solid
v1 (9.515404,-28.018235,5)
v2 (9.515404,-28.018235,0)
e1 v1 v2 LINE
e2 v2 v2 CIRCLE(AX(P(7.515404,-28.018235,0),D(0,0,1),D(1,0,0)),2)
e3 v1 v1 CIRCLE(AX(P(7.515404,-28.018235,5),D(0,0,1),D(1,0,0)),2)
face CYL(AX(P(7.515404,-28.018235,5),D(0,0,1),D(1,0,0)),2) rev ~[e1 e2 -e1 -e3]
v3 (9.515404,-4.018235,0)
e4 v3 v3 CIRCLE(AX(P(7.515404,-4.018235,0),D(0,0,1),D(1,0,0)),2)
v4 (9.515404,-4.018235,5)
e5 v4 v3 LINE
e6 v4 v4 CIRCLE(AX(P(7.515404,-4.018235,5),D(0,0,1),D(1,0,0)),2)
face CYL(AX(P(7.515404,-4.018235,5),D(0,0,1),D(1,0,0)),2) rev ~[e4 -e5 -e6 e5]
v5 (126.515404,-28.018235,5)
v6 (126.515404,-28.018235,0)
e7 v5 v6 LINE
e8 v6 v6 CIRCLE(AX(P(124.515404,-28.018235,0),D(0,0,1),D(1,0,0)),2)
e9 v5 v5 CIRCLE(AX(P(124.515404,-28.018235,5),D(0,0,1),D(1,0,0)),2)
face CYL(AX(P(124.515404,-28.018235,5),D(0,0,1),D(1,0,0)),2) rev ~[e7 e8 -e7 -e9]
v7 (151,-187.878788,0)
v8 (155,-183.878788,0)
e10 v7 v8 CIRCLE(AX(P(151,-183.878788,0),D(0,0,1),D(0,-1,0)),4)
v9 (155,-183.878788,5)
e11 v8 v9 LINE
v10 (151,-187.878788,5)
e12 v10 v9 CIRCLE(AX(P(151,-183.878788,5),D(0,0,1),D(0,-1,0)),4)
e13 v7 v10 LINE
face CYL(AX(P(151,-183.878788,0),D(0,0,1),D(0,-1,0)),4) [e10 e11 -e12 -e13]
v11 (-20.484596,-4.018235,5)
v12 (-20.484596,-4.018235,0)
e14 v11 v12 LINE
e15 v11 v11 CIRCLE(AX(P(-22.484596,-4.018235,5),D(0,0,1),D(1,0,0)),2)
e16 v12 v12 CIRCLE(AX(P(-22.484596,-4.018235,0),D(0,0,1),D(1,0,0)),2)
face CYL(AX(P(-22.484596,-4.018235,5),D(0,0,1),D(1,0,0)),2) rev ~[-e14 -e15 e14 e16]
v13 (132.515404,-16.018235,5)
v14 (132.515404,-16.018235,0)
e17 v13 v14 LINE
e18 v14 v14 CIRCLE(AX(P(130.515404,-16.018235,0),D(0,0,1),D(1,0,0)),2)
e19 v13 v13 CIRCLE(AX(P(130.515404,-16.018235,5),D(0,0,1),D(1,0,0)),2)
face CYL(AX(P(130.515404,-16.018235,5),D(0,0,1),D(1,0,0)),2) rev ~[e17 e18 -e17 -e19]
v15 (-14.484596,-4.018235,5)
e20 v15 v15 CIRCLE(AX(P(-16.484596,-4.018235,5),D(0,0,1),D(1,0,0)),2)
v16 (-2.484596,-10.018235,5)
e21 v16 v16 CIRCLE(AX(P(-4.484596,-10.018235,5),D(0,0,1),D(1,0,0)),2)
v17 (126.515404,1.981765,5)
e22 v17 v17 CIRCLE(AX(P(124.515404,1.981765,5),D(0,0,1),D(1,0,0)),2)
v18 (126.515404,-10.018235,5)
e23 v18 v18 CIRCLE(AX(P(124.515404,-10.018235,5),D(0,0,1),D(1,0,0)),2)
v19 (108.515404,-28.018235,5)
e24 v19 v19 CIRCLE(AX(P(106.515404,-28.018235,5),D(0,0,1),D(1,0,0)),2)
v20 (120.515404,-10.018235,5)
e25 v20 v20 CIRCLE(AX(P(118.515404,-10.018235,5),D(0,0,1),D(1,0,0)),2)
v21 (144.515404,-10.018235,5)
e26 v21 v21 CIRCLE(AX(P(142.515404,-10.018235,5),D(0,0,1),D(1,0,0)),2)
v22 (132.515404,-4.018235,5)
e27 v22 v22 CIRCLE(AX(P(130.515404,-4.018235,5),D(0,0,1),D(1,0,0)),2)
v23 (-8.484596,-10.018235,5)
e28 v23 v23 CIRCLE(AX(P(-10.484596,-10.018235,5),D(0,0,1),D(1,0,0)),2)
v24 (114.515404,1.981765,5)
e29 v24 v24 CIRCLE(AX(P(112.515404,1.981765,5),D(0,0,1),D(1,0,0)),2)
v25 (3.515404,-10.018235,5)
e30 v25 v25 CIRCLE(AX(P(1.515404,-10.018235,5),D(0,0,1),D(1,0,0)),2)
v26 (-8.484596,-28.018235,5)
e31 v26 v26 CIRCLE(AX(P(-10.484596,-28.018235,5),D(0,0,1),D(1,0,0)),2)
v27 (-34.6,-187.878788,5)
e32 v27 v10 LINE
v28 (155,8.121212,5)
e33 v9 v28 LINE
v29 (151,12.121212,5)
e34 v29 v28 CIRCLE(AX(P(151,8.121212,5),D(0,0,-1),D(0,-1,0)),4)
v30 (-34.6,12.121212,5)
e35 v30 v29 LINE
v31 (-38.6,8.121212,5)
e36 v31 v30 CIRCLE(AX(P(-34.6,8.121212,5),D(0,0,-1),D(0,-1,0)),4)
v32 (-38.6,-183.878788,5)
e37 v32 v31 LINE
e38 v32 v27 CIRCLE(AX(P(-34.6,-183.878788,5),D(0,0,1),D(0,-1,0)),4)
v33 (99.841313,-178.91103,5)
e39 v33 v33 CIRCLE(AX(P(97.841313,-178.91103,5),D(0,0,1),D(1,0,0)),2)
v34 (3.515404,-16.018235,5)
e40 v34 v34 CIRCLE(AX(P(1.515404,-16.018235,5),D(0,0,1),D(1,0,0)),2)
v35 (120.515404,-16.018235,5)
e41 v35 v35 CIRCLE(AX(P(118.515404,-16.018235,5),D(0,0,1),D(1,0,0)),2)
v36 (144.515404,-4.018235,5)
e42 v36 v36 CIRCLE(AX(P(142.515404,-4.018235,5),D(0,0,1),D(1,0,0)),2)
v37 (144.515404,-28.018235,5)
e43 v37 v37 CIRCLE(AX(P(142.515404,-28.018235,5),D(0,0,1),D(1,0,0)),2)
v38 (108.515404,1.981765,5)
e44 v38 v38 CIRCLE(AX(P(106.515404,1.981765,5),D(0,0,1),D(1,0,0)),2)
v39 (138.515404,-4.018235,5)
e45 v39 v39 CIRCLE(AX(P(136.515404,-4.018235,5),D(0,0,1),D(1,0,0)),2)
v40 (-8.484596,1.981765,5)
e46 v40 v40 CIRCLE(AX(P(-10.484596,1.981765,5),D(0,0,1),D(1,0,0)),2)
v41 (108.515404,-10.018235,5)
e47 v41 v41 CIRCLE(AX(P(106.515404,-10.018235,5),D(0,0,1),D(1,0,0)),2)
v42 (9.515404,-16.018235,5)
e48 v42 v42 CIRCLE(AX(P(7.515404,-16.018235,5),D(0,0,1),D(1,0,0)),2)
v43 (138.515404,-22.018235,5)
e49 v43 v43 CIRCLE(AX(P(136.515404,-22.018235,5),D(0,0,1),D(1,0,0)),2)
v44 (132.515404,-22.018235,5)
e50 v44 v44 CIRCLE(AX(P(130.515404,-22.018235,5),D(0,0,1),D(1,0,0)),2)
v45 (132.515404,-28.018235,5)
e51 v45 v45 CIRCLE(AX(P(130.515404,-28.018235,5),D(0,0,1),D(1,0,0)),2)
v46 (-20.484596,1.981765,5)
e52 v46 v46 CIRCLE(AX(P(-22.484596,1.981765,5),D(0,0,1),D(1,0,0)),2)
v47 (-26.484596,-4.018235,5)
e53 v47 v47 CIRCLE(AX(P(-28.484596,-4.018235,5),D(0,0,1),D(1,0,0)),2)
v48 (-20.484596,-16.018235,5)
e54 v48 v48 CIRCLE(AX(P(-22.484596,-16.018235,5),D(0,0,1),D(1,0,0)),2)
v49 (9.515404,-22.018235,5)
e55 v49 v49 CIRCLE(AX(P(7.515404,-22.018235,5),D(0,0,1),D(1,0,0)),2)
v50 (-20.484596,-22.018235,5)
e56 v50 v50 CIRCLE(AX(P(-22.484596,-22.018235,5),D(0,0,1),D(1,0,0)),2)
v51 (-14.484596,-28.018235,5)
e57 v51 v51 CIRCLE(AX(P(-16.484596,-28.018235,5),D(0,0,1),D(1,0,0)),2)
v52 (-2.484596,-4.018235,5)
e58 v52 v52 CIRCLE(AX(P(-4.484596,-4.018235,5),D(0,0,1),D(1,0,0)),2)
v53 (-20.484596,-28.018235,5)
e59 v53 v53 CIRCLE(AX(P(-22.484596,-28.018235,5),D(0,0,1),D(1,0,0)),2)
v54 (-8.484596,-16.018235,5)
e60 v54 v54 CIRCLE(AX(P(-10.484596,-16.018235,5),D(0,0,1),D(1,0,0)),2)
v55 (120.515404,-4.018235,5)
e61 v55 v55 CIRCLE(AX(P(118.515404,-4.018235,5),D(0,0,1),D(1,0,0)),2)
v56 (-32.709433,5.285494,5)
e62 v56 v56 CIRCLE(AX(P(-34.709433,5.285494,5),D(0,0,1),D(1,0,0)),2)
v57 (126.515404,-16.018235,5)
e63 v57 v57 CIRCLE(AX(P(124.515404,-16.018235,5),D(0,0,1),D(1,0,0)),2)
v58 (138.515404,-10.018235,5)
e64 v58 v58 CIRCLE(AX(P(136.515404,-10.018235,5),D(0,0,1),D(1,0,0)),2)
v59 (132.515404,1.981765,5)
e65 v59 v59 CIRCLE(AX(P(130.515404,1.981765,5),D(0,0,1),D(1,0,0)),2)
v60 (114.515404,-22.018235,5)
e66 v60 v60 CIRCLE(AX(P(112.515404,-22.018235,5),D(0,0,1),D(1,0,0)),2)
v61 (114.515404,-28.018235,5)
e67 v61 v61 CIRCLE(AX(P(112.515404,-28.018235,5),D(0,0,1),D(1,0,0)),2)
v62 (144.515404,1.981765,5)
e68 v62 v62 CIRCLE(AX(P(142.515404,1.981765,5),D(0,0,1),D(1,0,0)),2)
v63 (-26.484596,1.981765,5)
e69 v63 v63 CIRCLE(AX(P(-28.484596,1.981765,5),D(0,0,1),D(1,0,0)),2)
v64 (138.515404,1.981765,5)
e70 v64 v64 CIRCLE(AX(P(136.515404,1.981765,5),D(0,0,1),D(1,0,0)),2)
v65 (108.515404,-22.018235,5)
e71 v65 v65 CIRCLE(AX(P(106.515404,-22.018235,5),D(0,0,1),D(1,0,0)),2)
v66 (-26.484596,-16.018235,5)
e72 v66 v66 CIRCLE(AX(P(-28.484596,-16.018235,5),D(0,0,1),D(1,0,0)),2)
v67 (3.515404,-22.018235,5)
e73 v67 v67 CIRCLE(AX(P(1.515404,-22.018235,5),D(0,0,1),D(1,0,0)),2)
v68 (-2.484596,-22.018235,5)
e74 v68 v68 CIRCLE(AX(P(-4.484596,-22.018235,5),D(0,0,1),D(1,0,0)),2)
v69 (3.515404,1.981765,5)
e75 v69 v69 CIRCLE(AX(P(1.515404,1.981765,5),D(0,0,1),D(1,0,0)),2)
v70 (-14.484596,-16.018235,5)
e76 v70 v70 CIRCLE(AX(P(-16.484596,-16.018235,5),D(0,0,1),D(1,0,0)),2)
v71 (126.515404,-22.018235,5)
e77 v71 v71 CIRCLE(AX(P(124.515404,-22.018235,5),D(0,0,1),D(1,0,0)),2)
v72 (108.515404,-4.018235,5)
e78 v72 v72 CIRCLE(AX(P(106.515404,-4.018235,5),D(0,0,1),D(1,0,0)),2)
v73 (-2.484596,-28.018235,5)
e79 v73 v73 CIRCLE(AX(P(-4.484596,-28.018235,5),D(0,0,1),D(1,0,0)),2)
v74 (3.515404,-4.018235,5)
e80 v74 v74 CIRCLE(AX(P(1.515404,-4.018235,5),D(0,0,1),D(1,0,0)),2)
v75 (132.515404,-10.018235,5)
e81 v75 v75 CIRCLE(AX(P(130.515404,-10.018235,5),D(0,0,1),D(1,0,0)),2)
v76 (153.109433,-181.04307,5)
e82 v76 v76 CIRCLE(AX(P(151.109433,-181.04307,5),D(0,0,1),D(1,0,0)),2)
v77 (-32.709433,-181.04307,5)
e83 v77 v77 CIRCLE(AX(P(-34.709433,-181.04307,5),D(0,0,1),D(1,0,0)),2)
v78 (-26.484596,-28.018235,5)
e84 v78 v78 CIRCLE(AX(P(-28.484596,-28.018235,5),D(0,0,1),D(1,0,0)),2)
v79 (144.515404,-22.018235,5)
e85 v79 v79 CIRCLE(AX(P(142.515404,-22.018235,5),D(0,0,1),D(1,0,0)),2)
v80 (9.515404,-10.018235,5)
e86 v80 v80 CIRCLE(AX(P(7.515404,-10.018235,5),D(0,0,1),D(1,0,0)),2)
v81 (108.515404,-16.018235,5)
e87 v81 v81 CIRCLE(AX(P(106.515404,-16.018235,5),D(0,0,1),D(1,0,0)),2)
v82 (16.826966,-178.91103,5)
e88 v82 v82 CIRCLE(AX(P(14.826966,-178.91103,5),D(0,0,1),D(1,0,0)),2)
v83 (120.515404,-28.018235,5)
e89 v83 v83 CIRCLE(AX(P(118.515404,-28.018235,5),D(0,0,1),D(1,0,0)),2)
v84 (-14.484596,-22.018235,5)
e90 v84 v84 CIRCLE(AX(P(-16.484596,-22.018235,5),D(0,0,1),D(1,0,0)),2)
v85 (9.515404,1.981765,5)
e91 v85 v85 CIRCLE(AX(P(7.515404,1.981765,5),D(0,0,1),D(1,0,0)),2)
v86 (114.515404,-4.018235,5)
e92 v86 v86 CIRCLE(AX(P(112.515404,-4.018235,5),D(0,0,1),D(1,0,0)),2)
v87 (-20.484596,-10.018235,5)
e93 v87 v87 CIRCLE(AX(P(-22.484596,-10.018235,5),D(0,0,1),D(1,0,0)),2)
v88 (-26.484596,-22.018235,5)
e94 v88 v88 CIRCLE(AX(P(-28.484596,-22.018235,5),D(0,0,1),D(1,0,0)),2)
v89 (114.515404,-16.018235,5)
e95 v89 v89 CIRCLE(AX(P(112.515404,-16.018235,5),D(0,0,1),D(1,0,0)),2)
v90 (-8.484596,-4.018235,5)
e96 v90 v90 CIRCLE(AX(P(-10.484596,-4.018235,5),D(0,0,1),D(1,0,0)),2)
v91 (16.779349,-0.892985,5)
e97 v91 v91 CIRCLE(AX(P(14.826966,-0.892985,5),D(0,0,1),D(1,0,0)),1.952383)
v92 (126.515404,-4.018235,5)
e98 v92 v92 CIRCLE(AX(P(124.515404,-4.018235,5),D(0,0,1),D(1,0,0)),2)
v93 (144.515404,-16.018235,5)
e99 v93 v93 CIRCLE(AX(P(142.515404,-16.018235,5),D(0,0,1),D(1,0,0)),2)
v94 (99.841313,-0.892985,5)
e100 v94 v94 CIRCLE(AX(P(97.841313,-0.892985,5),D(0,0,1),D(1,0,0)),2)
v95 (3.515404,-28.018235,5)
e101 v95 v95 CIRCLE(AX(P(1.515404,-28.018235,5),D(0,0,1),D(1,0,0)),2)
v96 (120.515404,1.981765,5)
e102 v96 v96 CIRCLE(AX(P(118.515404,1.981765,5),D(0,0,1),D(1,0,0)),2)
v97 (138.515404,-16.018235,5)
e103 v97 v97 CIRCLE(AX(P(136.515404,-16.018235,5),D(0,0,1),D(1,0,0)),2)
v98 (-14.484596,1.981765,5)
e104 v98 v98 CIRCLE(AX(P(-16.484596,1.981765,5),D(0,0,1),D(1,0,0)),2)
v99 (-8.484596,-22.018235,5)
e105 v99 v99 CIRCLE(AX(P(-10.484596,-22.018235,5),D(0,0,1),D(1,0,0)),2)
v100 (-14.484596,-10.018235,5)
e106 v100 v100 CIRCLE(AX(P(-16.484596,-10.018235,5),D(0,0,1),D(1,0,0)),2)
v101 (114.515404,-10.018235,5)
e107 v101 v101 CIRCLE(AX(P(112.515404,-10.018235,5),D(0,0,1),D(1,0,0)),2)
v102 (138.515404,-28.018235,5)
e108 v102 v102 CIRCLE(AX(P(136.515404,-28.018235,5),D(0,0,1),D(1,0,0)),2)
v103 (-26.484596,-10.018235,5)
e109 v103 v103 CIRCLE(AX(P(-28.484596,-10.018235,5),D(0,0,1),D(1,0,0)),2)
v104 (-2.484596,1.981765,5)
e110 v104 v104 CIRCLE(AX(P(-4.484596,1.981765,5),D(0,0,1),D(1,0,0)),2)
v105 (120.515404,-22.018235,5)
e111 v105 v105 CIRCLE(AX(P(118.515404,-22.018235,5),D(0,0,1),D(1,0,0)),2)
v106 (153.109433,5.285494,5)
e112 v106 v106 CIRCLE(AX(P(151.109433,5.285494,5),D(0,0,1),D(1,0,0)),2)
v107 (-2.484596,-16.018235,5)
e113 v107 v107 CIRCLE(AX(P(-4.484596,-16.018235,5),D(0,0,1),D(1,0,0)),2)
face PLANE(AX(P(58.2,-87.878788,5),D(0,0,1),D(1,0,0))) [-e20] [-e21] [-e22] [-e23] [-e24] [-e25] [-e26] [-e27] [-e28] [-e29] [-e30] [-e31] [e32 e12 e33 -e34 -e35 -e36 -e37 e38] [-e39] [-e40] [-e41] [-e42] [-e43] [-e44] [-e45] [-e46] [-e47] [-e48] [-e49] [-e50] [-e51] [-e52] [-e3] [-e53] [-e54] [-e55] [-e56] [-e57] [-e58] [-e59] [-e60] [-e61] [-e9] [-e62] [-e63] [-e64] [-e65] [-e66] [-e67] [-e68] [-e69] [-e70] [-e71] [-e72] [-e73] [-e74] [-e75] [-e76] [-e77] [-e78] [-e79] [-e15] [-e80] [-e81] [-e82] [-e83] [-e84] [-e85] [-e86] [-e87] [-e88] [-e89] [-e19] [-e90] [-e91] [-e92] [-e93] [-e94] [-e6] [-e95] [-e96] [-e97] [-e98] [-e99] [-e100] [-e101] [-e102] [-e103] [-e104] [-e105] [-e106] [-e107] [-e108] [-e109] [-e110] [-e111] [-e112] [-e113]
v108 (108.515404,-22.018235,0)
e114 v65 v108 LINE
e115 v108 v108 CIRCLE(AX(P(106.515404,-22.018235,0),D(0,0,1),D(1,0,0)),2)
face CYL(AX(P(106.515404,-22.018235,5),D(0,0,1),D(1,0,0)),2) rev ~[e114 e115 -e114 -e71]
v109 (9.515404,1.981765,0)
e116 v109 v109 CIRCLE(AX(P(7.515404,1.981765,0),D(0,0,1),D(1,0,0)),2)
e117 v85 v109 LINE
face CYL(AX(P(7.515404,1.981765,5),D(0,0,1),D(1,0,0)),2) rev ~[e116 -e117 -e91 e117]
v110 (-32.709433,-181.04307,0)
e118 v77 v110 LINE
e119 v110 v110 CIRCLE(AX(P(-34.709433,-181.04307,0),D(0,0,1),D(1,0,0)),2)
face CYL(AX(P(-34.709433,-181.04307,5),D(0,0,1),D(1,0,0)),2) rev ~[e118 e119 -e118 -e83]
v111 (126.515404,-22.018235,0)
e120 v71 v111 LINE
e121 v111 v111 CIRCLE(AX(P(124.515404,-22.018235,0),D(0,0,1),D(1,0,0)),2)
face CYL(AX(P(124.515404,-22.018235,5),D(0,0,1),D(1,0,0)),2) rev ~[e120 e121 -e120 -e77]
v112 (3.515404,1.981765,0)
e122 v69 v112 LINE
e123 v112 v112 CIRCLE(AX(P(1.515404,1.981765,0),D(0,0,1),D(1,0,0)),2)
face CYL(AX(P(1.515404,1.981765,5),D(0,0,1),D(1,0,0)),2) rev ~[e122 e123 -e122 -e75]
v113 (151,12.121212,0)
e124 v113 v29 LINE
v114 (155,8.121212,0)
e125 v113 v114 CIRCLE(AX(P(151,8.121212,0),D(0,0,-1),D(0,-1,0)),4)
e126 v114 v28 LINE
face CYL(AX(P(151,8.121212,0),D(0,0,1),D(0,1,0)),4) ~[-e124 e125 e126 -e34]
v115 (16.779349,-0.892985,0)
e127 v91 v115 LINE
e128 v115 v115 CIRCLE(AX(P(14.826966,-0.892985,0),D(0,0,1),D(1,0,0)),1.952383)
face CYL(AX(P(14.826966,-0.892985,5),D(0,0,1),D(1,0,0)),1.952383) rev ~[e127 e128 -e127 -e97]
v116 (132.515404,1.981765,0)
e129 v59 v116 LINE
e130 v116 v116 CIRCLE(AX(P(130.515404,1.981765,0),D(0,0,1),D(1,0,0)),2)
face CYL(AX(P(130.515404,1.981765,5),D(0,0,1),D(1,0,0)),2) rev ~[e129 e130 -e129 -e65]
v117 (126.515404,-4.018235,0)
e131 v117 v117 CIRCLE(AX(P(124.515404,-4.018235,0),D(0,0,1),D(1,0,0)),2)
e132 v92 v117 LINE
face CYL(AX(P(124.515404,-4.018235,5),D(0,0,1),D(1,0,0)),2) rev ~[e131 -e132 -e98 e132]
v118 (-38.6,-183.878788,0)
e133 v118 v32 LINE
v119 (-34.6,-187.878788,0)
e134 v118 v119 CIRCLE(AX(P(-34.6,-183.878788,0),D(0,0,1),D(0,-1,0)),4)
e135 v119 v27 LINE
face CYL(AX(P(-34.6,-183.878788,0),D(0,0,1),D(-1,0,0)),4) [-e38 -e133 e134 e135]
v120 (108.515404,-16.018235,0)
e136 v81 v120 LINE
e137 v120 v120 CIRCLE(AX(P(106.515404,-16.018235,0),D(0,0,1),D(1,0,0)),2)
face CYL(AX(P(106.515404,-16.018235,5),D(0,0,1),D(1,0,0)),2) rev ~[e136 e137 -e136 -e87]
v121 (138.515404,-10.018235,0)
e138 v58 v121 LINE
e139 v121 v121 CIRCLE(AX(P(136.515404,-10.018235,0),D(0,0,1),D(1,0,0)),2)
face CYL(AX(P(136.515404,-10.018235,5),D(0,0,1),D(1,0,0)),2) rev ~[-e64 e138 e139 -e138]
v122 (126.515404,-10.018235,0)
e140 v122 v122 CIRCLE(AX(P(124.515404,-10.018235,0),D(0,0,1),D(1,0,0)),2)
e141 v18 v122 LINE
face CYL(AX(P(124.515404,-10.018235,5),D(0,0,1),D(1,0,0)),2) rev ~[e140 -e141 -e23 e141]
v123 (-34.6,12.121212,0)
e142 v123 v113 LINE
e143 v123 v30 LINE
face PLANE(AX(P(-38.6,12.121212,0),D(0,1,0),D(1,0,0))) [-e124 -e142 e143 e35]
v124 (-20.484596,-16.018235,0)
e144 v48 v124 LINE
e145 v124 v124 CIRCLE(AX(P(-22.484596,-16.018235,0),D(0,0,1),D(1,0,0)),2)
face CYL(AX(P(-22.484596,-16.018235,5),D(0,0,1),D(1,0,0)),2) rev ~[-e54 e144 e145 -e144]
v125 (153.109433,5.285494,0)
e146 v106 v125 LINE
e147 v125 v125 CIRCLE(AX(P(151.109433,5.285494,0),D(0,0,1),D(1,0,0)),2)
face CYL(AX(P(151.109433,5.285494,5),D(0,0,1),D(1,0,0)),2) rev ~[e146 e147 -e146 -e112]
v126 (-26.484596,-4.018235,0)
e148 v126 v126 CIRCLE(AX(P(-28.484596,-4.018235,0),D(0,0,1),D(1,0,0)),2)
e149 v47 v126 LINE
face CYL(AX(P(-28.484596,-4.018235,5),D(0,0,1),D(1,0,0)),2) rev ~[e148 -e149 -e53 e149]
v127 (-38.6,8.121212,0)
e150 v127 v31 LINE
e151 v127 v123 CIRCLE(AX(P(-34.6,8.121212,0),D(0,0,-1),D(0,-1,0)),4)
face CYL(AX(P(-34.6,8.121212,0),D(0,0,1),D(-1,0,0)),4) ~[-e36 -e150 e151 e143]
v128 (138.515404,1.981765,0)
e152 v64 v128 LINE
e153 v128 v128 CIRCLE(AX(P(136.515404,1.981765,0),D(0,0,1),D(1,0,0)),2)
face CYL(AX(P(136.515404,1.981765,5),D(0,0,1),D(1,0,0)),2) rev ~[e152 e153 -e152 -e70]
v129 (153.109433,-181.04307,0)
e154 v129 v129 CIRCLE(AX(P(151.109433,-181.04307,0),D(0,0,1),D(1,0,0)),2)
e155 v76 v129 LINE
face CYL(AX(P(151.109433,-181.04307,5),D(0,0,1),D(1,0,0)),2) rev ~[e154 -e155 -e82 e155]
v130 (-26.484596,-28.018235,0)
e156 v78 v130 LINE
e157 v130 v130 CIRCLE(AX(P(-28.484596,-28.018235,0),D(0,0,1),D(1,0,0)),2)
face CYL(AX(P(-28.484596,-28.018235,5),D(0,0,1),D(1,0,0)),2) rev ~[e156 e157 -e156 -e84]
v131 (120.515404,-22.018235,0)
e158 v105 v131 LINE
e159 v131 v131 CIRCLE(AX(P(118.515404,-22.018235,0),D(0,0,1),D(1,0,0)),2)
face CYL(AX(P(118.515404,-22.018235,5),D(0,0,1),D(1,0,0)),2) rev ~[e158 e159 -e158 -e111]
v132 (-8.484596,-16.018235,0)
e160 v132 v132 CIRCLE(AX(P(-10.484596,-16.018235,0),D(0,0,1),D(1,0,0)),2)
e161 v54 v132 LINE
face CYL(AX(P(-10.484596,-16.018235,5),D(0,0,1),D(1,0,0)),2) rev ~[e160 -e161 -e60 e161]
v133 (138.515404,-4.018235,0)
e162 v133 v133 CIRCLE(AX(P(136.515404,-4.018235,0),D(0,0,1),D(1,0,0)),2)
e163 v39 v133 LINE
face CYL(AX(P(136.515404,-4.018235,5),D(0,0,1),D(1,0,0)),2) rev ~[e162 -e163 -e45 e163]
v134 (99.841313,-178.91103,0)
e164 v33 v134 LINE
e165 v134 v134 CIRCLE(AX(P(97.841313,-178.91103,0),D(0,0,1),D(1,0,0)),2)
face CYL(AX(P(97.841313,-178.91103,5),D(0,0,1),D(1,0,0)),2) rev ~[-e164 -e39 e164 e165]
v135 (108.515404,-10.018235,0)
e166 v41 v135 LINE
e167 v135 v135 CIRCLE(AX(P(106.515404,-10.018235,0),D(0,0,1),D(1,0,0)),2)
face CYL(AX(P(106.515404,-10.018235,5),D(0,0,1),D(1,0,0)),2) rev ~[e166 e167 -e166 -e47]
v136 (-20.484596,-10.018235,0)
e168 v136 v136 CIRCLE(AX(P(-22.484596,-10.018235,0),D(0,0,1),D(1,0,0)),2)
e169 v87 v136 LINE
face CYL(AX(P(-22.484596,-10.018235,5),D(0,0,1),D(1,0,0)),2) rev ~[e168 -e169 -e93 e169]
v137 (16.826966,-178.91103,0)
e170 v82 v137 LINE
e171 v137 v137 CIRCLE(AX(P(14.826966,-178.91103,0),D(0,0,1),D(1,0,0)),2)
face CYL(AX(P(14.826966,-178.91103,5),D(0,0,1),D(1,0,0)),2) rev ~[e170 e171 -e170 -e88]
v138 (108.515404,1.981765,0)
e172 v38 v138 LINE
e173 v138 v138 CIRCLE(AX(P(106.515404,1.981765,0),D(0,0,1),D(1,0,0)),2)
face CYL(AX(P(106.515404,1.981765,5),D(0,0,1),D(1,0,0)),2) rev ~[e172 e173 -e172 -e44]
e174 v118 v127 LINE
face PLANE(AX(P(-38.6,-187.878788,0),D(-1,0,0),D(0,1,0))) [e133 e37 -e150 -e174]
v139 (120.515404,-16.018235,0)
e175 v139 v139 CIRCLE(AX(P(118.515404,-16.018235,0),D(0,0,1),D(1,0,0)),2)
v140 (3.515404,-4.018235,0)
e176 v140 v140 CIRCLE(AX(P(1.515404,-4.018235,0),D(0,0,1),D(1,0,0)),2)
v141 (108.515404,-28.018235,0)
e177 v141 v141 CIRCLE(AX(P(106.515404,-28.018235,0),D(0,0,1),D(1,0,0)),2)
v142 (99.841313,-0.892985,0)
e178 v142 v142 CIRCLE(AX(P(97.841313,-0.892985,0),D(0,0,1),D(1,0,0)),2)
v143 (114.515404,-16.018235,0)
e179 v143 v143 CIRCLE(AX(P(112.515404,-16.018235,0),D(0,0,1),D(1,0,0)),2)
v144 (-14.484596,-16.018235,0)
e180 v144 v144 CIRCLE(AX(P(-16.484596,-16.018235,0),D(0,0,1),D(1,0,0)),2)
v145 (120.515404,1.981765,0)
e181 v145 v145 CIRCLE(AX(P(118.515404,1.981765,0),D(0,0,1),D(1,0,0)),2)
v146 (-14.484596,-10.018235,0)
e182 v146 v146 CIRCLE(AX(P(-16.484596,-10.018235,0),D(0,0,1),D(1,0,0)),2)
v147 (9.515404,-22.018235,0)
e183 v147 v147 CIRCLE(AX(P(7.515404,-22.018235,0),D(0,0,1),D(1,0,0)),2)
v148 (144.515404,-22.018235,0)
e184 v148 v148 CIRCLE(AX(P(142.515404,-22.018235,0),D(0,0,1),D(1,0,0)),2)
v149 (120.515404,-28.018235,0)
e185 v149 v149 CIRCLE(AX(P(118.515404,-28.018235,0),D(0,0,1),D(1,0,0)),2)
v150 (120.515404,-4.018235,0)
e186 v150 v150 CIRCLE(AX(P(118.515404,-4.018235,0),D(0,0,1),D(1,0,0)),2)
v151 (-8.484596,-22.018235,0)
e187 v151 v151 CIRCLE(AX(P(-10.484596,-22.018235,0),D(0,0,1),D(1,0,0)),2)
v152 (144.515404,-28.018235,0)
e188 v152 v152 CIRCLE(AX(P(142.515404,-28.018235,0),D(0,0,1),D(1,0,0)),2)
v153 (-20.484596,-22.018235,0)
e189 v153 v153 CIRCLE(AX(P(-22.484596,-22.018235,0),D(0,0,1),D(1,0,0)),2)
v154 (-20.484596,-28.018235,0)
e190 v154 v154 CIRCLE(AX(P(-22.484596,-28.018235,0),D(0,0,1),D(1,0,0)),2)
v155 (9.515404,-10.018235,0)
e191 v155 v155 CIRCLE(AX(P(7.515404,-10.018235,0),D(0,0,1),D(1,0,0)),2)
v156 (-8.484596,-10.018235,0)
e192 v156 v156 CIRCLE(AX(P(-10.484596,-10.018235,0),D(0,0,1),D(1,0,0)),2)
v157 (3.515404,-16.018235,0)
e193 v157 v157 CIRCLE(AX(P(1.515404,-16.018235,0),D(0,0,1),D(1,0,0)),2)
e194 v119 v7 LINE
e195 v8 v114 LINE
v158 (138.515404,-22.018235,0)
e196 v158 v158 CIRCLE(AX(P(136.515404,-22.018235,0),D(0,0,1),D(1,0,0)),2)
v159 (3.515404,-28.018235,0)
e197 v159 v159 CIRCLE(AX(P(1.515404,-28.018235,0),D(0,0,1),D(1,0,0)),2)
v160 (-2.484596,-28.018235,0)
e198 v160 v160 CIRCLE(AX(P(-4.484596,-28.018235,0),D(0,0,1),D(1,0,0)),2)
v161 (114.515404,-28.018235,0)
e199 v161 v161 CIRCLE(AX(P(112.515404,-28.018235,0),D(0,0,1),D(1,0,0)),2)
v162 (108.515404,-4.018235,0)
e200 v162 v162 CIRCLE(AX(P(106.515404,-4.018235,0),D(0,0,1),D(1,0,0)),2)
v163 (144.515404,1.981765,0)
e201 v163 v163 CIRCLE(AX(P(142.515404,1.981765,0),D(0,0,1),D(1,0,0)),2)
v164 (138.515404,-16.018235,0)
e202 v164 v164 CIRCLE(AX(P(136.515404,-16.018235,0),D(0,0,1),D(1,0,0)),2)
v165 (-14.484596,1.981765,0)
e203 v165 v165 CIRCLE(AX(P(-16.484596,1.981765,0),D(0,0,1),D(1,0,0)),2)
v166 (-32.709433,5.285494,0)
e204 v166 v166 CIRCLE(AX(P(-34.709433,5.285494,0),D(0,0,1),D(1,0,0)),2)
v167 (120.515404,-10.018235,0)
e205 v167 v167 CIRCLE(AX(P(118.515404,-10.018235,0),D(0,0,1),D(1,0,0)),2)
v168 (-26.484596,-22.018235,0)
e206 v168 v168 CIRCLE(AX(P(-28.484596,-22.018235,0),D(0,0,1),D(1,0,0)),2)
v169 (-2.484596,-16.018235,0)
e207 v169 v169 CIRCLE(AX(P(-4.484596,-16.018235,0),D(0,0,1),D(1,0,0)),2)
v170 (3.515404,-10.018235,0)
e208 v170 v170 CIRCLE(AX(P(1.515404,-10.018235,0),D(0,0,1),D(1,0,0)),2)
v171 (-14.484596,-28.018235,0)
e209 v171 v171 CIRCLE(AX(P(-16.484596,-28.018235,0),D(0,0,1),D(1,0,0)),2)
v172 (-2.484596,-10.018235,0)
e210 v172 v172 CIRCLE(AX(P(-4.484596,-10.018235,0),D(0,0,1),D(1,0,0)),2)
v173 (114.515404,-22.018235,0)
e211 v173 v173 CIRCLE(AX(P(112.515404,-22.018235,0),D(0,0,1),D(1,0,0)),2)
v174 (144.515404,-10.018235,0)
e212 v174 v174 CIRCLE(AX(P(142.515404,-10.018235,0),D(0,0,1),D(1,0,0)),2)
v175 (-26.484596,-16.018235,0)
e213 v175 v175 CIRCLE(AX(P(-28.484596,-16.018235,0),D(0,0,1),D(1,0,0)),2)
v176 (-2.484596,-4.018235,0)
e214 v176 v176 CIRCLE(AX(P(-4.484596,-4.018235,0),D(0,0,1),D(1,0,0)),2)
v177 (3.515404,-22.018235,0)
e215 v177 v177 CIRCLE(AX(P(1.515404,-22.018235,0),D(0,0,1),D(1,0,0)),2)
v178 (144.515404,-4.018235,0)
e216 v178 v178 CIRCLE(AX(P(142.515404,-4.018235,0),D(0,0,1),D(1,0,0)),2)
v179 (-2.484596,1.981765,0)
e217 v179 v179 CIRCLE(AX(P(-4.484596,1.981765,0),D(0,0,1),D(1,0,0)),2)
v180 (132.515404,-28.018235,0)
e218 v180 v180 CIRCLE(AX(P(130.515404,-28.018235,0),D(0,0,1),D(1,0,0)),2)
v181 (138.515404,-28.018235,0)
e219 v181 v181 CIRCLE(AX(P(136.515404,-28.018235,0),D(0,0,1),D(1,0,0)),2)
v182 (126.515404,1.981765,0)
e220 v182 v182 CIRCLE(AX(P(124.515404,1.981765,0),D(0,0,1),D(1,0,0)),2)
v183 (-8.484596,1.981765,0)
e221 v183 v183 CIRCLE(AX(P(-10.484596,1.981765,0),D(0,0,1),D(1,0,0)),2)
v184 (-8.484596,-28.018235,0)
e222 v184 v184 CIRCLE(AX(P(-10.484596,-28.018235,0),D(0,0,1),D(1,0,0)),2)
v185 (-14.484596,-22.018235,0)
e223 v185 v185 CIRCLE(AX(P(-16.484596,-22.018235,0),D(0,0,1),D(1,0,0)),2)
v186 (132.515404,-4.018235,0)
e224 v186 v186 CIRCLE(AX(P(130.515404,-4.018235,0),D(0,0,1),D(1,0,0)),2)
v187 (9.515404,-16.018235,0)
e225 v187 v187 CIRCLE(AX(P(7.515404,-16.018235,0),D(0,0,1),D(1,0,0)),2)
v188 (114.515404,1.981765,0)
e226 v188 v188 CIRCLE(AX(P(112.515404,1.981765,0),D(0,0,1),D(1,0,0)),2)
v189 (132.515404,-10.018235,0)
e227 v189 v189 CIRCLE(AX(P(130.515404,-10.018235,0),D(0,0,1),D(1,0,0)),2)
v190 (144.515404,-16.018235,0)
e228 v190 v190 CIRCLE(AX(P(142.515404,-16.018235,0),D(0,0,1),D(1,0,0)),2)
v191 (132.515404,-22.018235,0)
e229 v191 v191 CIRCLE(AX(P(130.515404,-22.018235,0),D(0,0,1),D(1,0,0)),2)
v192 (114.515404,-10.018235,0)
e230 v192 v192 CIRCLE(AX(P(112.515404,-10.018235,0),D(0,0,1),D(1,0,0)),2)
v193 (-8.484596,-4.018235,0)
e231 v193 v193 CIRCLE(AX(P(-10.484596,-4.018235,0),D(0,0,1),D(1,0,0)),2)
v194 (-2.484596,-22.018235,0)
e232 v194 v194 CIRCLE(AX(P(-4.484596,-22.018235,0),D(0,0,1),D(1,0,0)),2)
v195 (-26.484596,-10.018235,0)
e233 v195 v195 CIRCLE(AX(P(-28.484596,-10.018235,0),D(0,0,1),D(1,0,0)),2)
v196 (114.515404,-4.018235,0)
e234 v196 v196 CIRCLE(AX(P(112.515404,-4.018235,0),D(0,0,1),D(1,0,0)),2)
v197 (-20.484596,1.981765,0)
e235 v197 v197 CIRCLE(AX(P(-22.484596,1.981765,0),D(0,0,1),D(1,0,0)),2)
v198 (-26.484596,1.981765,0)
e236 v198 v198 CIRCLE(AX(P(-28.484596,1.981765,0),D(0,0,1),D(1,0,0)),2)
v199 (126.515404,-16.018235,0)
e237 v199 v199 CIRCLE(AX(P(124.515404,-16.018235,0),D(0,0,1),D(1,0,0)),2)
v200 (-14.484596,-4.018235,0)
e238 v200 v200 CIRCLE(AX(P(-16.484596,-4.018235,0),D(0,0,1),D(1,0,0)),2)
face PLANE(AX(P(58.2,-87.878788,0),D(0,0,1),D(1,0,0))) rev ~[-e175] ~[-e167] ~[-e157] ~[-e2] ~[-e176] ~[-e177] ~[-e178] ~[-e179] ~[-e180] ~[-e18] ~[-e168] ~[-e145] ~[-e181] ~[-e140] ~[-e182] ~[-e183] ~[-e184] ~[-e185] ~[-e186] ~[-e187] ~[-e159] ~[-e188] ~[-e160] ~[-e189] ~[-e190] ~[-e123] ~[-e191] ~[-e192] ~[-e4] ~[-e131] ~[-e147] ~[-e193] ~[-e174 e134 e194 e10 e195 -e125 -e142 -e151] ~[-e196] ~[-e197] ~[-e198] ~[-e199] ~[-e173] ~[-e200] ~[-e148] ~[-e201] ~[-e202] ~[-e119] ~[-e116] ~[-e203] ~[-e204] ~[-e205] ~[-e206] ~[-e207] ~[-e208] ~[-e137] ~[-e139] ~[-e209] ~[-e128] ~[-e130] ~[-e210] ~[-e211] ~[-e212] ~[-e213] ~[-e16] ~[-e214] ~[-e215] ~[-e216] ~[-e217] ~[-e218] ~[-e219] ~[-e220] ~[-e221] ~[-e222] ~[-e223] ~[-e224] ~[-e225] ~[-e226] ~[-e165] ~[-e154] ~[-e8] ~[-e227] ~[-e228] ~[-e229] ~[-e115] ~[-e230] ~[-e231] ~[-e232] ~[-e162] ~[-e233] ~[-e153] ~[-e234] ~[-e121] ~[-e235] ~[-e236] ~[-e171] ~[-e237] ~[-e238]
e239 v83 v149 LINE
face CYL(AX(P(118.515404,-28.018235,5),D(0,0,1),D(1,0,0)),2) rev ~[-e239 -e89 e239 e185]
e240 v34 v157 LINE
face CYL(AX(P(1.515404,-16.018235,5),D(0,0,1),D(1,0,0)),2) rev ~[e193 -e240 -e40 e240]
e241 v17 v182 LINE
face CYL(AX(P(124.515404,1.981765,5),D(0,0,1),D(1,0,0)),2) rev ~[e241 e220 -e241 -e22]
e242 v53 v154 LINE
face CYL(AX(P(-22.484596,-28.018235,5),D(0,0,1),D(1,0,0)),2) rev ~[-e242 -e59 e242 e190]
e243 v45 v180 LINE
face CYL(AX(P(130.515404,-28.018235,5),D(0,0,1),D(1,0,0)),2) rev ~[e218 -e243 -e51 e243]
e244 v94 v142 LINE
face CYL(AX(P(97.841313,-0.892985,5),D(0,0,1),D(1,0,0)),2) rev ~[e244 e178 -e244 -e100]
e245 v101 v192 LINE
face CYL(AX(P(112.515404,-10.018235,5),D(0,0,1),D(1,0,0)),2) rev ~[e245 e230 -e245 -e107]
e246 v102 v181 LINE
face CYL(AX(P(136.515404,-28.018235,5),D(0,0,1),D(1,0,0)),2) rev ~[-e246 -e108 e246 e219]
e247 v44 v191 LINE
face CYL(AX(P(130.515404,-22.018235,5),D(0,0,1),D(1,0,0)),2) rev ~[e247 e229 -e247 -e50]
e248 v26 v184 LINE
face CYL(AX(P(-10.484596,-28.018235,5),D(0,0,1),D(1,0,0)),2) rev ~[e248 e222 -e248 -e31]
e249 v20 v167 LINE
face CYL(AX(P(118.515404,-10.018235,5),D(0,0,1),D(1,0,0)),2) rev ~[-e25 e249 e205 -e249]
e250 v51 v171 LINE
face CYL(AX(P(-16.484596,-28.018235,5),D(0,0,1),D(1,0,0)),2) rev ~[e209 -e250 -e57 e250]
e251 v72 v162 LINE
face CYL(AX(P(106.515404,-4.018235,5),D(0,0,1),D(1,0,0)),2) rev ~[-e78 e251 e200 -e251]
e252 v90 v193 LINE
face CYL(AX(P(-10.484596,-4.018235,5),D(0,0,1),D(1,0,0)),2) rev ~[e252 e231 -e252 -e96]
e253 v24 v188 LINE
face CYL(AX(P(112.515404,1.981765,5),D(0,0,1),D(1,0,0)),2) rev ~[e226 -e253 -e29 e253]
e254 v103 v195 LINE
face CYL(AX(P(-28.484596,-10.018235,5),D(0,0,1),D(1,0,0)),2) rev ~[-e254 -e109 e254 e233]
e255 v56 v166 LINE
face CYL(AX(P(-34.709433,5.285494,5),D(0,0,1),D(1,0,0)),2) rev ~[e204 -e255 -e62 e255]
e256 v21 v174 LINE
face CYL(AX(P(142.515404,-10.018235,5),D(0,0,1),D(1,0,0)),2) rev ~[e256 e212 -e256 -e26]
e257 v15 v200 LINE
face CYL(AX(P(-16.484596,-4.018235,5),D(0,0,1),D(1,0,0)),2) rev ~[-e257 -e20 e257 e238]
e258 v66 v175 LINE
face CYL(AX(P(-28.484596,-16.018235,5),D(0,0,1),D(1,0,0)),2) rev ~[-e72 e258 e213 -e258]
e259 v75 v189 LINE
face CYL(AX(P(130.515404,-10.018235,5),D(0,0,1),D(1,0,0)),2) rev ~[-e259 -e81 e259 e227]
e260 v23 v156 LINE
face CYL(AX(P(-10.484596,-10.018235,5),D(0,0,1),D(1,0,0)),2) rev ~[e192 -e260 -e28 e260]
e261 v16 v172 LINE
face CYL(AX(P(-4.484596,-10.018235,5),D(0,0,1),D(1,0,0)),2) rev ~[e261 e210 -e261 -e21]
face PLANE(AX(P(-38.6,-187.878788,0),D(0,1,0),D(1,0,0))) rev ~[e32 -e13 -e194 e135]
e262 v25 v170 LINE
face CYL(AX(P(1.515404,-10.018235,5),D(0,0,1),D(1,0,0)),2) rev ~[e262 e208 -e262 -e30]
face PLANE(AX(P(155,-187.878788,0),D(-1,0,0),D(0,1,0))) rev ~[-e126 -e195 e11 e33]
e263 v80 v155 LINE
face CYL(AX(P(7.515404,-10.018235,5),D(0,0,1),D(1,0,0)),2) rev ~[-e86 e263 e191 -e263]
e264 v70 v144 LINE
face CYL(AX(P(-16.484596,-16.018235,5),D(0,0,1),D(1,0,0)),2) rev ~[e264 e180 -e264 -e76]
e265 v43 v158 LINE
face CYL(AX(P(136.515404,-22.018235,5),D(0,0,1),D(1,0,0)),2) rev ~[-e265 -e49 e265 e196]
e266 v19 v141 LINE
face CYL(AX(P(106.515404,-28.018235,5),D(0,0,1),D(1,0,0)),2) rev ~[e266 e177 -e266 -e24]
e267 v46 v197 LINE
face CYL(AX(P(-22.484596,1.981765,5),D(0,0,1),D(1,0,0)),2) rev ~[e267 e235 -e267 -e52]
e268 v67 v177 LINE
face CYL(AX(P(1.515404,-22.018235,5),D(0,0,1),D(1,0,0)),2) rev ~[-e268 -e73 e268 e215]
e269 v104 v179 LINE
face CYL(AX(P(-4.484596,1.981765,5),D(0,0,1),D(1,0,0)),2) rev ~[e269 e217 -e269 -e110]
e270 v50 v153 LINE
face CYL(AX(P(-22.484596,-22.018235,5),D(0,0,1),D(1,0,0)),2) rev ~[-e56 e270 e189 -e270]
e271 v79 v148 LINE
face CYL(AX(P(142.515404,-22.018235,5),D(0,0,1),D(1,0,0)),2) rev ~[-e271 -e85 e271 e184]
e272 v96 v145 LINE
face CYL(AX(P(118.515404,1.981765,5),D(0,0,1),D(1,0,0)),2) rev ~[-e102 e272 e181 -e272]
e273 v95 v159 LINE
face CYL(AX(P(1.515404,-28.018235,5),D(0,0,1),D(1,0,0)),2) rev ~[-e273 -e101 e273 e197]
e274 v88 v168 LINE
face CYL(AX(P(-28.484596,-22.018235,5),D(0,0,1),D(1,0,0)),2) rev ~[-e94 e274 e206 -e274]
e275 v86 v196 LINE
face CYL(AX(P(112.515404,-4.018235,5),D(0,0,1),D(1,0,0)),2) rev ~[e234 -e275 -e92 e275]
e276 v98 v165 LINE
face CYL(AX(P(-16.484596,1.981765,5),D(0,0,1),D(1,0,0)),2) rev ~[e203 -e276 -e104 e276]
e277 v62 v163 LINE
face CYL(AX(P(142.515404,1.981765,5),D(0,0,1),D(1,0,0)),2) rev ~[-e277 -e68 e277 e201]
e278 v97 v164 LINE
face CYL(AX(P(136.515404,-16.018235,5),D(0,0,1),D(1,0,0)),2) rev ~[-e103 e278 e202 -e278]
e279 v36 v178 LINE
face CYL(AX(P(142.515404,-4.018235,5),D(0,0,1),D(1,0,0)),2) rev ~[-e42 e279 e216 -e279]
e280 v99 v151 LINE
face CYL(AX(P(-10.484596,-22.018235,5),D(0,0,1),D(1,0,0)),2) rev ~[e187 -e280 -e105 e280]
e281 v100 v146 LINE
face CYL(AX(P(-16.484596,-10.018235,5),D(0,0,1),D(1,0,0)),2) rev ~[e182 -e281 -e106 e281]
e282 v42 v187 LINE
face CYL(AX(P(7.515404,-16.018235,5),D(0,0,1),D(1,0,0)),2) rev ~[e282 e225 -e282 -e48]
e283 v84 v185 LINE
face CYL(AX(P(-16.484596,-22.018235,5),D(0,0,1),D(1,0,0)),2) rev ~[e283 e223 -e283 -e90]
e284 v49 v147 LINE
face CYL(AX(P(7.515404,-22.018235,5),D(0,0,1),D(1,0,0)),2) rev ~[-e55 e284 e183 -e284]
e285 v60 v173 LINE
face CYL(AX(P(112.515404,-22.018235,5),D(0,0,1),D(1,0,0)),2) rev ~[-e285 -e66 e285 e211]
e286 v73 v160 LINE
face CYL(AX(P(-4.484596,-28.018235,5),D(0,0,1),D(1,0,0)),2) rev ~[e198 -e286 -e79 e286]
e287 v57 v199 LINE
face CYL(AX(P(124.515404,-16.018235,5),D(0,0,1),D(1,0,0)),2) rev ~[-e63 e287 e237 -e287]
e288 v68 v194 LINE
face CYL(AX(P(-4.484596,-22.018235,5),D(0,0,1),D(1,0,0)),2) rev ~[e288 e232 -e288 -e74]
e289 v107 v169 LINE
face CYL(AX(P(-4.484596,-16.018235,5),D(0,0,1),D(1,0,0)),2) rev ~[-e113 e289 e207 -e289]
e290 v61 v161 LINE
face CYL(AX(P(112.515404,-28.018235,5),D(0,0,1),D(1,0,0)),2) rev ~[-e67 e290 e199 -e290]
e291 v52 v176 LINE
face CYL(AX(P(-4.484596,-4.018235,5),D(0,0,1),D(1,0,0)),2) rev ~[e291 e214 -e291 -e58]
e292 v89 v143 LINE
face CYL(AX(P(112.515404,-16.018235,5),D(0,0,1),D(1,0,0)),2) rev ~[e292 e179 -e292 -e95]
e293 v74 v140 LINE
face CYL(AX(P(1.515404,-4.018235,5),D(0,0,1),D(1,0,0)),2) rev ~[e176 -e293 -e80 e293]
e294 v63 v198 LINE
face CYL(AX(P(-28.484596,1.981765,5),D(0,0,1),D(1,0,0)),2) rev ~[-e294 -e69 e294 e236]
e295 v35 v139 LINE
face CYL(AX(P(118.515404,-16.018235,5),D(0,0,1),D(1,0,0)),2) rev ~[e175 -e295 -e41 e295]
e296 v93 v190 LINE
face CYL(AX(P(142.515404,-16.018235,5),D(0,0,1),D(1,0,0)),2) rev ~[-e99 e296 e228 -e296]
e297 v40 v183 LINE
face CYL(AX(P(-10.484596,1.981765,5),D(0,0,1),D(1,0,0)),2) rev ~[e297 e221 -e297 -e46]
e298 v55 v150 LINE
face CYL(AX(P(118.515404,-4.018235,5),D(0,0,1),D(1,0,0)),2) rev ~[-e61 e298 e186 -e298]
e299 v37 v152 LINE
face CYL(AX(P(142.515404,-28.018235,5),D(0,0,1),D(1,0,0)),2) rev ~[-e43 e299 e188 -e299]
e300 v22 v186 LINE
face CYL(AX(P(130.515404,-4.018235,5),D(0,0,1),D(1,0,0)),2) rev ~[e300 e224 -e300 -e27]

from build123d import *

# Parameters (mm, degrees)
SKETCH1_W           = 193.6
SKETCH1_H           = 200
BOSS_EXTRUDE1_DEPTH = 5
SKETCH3_R           = 2
SKETCH3_R_2         = 1.952382978
CUT_EXTRUDE2_DEPTH  = 12
SKETCH4_R           = 2
CUT_EXTRUDE3_DEPTH  = 10
FILLET1_R           = 4
SKETCH5_R           = 2
CUT_EXTRUDE4_DEPTH  = 10
LPATTERN1_COUNT     = 2
LPATTERN1_PITCH     = 135


with BuildPart() as part:
    # Sketch1 → Boss-Extrude1 (new body)
    with BuildSketch(Plane.XY):
        with Locations((58.2, -87.878787879)):
            Rectangle(SKETCH1_W, SKETCH1_H)
    extrude(amount=BOSS_EXTRUDE1_DEPTH)

    # Sketch3 → Cut-Extrude2 (cut)
    with BuildSketch(Plane.XY.offset(5)):
        with Locations((97.841313089, -178.911029975)):
            Circle(SKETCH3_R)
        with Locations((97.841313089, -0.892985434)):
            Circle(SKETCH3_R)
        with Locations((14.826966281, -178.911029975)):
            Circle(SKETCH3_R)
        with Locations((14.826966281, -0.892985434)):
            Circle(SKETCH3_R_2)
    extrude(amount=-CUT_EXTRUDE2_DEPTH, mode=Mode.SUBTRACT)

    # Sketch4 → Cut-Extrude3 (cut)
    with BuildSketch(Plane.XY.offset(5)):
        with Locations((151.109433088, -181.043069679)):
            Circle(SKETCH4_R)
        with Locations((151.109433088, 5.285493921)):
            Circle(SKETCH4_R)
        with Locations((-34.709433088, 5.285493921)):
            Circle(SKETCH4_R)
        with Locations((-34.709433088, -181.043069679)):
            Circle(SKETCH4_R)
    extrude(amount=-CUT_EXTRUDE3_DEPTH, mode=Mode.SUBTRACT)

    # Fillet1
    fillet1_edges = [part.edges().sort_by_distance(p)[0] for p in [
        (-38.6, 12.121212121, 2.5),
        (155, 12.121212121, 2.5),
        (155, -187.878787879, 2.5),
        (-38.6, -187.878787879, 2.5),
    ]]
    fillet(fillet1_edges, radius=FILLET1_R)

    # Sketch5 → Cut-Extrude4 (cut)
    with BuildSketch(Plane.XY.offset(5)):
        with Locations((142.515403652, 1.981764562)):
            Circle(SKETCH5_R)
        with Locations((136.515403652, 1.981764562)):
            Circle(SKETCH5_R)
        with Locations((130.515403652, 1.981764562)):
            Circle(SKETCH5_R)
        with Locations((124.515403652, 1.981764562)):
            Circle(SKETCH5_R)
        with Locations((118.515403652, 1.981764562)):
            Circle(SKETCH5_R)
        with Locations((112.515403652, 1.981764562)):
            Circle(SKETCH5_R)
        with Locations((106.515403652, 1.981764562)):
            Circle(SKETCH5_R)
        with Locations((136.515403652, -4.018235438)):
            Circle(SKETCH5_R)
        with Locations((130.515403652, -4.018235438)):
            Circle(SKETCH5_R)
        with Locations((124.515403652, -4.018235438)):
            Circle(SKETCH5_R)
        with Locations((118.515403652, -4.018235438)):
            Circle(SKETCH5_R)
        with Locations((112.515403652, -4.018235438)):
            Circle(SKETCH5_R)
        with Locations((106.515403652, -4.018235438)):
            Circle(SKETCH5_R)
        with Locations((136.515403652, -10.018235438)):
            Circle(SKETCH5_R)
        with Locations((130.515403652, -10.018235438)):
            Circle(SKETCH5_R)
        with Locations((124.515403652, -10.018235438)):
            Circle(SKETCH5_R)
        with Locations((118.515403652, -10.018235438)):
            Circle(SKETCH5_R)
        with Locations((112.515403652, -10.018235438)):
            Circle(SKETCH5_R)
        with Locations((106.515403652, -10.018235438)):
            Circle(SKETCH5_R)
        with Locations((136.515403652, -16.018235438)):
            Circle(SKETCH5_R)
        with Locations((130.515403652, -16.018235438)):
            Circle(SKETCH5_R)
        with Locations((124.515403652, -16.018235438)):
            Circle(SKETCH5_R)
        with Locations((118.515403652, -16.018235438)):
            Circle(SKETCH5_R)
        with Locations((112.515403652, -16.018235438)):
            Circle(SKETCH5_R)
        with Locations((106.515403652, -16.018235438)):
            Circle(SKETCH5_R)
        with Locations((136.515403652, -22.018235438)):
            Circle(SKETCH5_R)
        with Locations((130.515403652, -22.018235438)):
            Circle(SKETCH5_R)
        with Locations((124.515403652, -22.018235438)):
            Circle(SKETCH5_R)
        with Locations((118.515403652, -22.018235438)):
            Circle(SKETCH5_R)
        with Locations((112.515403652, -22.018235438)):
            Circle(SKETCH5_R)
        with Locations((106.515403652, -22.018235438)):
            Circle(SKETCH5_R)
        with Locations((136.515403652, -28.018235438)):
            Circle(SKETCH5_R)
        with Locations((130.515403652, -28.018235438)):
            Circle(SKETCH5_R)
        with Locations((124.515403652, -28.018235438)):
            Circle(SKETCH5_R)
        with Locations((118.515403652, -28.018235438)):
            Circle(SKETCH5_R)
        with Locations((112.515403652, -28.018235438)):
            Circle(SKETCH5_R)
        with Locations((106.515403652, -28.018235438)):
            Circle(SKETCH5_R)
        with Locations((142.515403652, -4.018235438)):
            Circle(SKETCH5_R)
        with Locations((142.515403652, -10.018235438)):
            Circle(SKETCH5_R)
        with Locations((142.515403652, -16.018235438)):
            Circle(SKETCH5_R)
        with Locations((142.515403652, -22.018235438)):
            Circle(SKETCH5_R)
        with Locations((142.515403652, -28.018235438)):
            Circle(SKETCH5_R)
    cut_extrude4 = extrude(amount=-CUT_EXTRUDE4_DEPTH, mode=Mode.SUBTRACT)

    # LPattern1: Cut-Extrude4 ×2
    with Locations(*[(-i * LPATTERN1_PITCH, 0, 0) for i in range(1, LPATTERN1_COUNT)]):
        add(cut_extrude4, mode=Mode.SUBTRACT)


solid = part.part
